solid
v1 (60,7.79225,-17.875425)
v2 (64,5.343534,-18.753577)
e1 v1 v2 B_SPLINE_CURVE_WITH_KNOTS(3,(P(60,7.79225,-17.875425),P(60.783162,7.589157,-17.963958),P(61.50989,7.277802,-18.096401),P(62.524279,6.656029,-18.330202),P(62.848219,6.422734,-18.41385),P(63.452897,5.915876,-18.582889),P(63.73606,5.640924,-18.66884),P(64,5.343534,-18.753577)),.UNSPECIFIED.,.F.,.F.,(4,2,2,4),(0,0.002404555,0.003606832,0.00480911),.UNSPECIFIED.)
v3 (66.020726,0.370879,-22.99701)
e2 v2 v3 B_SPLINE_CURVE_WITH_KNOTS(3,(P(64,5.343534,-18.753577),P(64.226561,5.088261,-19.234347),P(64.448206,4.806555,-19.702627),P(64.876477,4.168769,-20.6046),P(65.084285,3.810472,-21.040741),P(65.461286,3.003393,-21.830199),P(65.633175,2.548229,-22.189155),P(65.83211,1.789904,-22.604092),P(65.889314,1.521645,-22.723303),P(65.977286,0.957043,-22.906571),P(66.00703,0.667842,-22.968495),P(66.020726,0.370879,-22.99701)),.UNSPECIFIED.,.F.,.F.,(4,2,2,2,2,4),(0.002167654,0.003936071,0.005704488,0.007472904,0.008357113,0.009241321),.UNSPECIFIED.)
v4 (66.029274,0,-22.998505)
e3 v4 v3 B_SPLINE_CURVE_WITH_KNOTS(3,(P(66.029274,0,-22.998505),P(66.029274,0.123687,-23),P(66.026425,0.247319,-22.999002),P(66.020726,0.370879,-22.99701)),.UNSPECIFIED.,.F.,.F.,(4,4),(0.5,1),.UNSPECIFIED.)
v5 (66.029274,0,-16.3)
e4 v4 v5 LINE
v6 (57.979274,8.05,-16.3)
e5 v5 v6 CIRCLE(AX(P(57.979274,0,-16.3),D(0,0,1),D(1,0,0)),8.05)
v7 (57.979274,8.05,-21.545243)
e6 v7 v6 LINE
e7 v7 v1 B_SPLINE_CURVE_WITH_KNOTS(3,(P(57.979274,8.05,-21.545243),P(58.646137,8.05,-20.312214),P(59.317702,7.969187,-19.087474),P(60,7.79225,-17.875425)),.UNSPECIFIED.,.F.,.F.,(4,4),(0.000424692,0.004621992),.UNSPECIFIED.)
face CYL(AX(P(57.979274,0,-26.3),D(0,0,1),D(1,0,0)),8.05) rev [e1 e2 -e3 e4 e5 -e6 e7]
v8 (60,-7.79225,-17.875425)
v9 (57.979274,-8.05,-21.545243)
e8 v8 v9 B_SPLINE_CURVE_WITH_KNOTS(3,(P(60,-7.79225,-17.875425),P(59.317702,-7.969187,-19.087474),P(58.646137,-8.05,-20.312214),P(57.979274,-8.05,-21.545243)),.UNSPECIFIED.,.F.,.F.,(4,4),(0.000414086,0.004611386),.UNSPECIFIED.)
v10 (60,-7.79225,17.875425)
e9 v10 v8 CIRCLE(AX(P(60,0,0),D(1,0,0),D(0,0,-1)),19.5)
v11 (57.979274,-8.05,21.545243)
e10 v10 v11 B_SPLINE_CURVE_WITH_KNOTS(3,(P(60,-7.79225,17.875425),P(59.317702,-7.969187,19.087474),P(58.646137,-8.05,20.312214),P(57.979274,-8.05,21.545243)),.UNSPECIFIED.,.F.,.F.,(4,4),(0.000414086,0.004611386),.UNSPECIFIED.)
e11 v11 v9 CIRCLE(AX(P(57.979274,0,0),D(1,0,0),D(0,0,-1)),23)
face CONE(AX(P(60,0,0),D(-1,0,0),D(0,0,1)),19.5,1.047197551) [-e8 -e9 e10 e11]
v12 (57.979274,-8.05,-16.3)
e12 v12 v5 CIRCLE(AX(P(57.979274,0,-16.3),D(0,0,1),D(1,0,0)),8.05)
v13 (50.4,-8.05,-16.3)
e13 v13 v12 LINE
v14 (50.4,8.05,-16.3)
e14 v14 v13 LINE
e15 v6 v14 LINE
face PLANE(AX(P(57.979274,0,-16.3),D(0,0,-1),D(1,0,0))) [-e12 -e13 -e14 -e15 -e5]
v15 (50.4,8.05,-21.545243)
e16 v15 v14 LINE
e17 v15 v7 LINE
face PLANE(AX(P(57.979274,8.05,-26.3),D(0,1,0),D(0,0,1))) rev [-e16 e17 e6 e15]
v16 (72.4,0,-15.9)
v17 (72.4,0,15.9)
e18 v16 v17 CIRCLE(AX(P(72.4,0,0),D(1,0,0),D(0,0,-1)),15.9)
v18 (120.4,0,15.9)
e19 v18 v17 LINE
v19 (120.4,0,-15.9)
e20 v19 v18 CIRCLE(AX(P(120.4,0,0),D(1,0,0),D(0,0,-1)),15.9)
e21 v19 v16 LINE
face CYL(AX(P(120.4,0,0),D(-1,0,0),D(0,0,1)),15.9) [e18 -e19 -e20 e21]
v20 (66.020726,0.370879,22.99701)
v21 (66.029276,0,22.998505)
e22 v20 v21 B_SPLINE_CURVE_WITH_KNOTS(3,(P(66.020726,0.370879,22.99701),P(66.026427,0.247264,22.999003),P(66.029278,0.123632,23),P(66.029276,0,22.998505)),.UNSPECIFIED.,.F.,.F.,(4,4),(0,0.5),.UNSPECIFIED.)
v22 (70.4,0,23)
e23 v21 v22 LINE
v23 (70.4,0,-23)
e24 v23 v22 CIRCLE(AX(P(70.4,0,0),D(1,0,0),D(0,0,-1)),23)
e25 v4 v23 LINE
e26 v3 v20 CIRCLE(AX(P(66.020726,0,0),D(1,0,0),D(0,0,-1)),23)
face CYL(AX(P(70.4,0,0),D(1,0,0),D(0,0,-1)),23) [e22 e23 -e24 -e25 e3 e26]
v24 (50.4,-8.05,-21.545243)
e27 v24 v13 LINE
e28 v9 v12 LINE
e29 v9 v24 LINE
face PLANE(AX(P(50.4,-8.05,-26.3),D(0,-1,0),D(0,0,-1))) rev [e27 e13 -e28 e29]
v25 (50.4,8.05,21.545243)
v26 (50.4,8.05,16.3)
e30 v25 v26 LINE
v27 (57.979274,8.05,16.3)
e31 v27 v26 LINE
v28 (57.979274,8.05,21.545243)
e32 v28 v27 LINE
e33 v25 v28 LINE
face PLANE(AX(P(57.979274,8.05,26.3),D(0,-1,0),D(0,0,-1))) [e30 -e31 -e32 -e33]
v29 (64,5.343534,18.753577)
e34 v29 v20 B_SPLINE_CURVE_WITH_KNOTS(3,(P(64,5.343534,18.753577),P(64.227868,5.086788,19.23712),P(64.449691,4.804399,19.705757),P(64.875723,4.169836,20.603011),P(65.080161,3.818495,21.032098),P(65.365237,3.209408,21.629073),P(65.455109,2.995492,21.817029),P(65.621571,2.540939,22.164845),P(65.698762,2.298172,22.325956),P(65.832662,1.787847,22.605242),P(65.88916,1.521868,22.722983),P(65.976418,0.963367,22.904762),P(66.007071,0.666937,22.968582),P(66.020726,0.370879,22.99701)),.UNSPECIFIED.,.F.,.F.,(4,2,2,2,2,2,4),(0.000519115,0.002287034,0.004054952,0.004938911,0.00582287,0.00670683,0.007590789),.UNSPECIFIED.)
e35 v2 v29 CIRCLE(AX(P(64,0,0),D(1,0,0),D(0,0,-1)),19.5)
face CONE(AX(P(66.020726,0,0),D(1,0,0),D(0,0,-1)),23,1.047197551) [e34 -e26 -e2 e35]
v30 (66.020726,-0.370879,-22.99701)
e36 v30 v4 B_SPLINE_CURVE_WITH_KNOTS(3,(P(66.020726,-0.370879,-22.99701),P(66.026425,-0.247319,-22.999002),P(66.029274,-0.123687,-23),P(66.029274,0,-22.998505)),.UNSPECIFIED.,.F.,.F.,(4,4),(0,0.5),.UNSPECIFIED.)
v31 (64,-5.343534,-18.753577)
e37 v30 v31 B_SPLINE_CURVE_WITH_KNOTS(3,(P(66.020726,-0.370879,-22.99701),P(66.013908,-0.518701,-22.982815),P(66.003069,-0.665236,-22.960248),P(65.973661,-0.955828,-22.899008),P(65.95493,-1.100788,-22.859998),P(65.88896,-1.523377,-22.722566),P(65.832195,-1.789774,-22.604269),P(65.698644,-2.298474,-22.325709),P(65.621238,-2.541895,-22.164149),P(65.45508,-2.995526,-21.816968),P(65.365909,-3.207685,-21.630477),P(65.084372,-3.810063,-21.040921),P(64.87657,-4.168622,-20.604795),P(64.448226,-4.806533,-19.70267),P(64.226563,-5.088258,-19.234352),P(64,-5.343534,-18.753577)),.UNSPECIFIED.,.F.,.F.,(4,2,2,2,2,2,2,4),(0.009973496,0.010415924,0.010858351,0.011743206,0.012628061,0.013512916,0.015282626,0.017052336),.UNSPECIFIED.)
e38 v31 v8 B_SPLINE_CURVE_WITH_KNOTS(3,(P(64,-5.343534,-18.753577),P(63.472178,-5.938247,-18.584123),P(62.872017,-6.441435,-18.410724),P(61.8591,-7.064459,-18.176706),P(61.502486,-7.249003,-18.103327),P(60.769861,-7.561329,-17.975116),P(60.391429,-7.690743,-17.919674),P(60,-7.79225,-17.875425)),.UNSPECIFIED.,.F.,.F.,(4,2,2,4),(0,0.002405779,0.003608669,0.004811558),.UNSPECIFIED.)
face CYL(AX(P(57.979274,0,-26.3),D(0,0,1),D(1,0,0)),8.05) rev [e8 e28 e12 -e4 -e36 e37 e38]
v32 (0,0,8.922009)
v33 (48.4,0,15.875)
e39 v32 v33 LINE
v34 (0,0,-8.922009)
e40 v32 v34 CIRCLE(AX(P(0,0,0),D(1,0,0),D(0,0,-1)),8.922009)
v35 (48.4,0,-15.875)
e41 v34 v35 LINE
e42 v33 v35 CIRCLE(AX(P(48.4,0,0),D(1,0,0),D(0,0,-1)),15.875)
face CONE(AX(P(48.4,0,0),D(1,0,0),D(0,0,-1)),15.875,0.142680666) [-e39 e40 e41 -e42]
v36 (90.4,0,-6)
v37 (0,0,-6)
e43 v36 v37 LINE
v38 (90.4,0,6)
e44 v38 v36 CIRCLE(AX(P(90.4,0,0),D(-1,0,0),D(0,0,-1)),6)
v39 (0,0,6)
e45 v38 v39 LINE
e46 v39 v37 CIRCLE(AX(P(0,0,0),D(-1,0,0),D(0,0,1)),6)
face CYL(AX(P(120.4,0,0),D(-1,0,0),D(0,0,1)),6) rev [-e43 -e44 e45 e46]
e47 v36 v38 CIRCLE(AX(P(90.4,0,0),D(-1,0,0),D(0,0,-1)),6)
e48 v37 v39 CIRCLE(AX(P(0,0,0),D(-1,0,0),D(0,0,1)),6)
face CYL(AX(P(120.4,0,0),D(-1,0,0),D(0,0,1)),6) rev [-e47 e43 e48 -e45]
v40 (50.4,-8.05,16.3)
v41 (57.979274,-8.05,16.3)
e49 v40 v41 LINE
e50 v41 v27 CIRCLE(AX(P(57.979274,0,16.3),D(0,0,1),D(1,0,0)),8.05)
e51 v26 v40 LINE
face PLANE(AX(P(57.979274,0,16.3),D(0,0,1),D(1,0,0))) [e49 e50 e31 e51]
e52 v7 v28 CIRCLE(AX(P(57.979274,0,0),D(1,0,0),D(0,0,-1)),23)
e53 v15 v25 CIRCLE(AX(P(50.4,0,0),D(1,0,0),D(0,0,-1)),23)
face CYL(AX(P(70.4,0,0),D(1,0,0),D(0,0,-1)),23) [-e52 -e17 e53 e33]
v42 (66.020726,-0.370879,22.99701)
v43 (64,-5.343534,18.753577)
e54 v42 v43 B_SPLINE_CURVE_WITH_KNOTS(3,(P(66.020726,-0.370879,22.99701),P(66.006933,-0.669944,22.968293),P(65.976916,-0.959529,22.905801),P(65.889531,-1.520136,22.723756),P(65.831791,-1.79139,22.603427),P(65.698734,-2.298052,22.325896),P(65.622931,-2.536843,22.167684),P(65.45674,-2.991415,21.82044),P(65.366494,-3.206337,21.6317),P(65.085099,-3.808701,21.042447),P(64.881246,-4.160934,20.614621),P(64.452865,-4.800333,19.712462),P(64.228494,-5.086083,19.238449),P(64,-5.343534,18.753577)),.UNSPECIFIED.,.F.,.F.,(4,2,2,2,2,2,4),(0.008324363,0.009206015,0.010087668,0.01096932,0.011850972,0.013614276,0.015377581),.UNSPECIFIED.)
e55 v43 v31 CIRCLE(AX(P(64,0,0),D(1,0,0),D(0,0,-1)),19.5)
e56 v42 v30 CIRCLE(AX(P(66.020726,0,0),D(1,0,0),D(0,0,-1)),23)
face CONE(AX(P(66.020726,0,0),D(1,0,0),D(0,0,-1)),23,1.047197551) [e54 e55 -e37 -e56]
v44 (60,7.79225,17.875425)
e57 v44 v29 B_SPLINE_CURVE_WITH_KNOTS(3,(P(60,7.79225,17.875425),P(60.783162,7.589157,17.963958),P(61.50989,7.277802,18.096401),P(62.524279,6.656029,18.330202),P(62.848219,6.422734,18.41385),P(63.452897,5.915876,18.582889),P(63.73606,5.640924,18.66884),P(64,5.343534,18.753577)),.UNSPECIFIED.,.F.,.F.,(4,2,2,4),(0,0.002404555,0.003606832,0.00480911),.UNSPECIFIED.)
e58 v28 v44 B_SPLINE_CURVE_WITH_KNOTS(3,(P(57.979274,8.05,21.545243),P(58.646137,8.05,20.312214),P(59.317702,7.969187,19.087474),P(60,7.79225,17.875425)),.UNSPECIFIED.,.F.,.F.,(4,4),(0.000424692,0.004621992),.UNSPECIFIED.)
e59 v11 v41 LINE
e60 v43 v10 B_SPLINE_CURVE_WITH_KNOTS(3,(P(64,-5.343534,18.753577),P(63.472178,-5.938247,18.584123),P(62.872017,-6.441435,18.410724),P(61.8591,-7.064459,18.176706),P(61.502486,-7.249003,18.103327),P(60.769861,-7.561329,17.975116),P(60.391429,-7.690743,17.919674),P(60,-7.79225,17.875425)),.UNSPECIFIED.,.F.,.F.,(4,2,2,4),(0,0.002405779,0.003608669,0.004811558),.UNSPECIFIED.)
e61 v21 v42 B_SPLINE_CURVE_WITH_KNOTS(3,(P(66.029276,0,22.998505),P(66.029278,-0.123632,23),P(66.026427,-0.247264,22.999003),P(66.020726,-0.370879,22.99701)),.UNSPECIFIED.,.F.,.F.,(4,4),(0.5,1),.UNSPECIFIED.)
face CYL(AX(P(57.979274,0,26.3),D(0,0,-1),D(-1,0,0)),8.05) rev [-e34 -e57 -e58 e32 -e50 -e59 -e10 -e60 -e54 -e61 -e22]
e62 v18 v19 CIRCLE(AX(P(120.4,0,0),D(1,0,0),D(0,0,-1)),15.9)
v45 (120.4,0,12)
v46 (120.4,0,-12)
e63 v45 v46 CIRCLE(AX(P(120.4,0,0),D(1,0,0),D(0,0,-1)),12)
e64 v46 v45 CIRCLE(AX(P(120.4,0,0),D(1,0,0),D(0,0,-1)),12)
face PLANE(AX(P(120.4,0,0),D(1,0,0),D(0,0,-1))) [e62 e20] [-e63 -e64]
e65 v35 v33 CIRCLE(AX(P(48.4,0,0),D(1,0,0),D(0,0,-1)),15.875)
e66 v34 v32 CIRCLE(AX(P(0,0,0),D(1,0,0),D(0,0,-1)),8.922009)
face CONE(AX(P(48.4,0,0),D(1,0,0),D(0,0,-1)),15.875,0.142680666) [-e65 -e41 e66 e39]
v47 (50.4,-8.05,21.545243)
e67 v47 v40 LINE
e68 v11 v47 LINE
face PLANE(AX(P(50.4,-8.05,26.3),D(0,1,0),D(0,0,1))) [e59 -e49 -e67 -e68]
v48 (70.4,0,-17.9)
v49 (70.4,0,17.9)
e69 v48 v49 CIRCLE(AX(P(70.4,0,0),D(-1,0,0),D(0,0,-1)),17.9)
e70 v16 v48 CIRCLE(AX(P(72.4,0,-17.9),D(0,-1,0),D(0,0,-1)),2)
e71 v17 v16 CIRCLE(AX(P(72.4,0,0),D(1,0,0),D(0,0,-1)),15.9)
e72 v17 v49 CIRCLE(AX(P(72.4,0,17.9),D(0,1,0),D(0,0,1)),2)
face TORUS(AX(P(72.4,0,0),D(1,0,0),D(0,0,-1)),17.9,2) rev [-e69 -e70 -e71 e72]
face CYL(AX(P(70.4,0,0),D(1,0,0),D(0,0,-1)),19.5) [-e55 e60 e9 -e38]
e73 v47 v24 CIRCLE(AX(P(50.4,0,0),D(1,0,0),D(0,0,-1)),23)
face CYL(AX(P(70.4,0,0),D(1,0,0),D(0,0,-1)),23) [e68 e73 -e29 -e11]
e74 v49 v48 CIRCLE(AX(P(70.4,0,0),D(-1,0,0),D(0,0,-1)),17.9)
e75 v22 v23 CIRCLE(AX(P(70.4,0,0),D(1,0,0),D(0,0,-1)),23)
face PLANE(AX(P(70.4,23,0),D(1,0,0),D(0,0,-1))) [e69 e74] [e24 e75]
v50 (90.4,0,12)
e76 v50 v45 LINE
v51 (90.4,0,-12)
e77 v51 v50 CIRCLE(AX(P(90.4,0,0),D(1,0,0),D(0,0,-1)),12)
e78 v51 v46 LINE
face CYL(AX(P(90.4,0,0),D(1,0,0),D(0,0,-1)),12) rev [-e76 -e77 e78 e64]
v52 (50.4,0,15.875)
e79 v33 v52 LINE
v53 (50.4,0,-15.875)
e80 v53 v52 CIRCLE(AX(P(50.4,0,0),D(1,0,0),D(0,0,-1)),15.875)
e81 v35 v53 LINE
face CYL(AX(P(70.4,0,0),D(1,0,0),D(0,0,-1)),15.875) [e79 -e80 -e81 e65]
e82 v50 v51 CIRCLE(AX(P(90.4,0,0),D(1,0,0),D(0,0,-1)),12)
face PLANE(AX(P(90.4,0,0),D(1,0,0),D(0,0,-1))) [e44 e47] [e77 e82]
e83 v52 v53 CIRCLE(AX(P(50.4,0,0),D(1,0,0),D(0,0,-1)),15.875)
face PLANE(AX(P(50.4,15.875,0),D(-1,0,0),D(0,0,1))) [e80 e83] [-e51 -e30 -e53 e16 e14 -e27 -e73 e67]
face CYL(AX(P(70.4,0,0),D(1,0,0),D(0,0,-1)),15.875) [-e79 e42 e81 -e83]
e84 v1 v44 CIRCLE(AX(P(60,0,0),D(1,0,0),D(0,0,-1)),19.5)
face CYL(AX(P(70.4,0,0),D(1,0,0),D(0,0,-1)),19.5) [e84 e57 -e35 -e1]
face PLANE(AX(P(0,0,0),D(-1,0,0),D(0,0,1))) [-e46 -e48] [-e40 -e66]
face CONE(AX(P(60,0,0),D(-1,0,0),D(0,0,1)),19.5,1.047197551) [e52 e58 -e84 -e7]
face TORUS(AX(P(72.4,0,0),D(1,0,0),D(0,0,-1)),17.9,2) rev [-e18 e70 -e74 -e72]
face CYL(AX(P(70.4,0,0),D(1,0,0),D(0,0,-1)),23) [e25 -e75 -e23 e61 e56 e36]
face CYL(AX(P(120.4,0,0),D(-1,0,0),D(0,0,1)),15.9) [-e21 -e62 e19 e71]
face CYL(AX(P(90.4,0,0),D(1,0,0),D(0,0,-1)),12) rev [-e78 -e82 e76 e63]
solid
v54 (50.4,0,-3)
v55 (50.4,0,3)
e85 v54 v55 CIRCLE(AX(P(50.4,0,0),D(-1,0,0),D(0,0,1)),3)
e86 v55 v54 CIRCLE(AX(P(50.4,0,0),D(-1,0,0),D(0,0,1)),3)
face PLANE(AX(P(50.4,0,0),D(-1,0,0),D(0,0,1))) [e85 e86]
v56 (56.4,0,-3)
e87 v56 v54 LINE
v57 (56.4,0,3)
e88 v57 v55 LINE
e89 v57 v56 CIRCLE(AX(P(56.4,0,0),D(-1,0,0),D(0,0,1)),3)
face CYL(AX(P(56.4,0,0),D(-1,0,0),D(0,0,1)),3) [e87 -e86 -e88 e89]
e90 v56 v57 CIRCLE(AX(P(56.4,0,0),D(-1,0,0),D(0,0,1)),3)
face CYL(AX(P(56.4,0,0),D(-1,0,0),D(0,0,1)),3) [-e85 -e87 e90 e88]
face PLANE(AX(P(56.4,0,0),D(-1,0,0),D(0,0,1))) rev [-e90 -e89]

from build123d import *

# Parameters (mm, degrees)
CUT_EXTRUDE_1_DEPTH = 10
SKETCH_4_R          = 15.9
EXTRUDE_1_DEPTH     = 50
FILLET_1_R          = 2
SKETCH_5_R          = 6
CUT_EXTRUDE_2_DEPTH = 125.716318135
SKETCH_6_R          = 12
CUT_EXTRUDE_3_DEPTH = 30
SKETCH_7_R          = 3
EXTRUDE_2_DEPTH     = 6


with BuildPart() as part:
    # 草图1 → 旋转1 (revolve)
    with BuildSketch(Plane.XY, mode=Mode.PRIVATE) as revolve_1_sk:
        Polygon((0, 0), (0, 8.92200912), (48.4, 15.875), (50.4, 15.875), (50.4, 23), (57.979274058, 23), (60, 19.5), (64, 19.5), (66.020725942, 23), (70.4, 23), (70.4, 0), align=None)
    revolve(revolve_1_sk.sketch.rotate(Axis((70.4, 0, 0), (-1, 0, 0)), 90), axis=Axis((70.4, 0, 0), (-1, 0, 0)))

    # 草图2 → 切除-拉伸1 (cut)
    with BuildSketch(Plane.XY.offset(16.3)):
        with BuildLine():
            Line((57.979274058, 8.05), (50.4, 8.05))
            Line((50.4, 8.05), (50.4, -8.05))
            Line((50.4, -8.05), (57.979274058, -8.05))
            ThreePointArc((57.979274058, -8.05), (66.029274058, 0), (57.979274058, 8.05))
        make_face()
    cut_extrude_1 = extrude(amount=CUT_EXTRUDE_1_DEPTH, mode=Mode.SUBTRACT)

    # 镜向1: 切除-拉伸1 across plane
    add(cut_extrude_1.mirror(Plane.XY), mode=Mode.SUBTRACT)

    # 草图4 → 凸台-拉伸1 (add)
    with BuildSketch(Plane(origin=(70.4, 0, 0), x_dir=(0, 0, -1), z_dir=(1, 0, 0))):
        Circle(SKETCH_4_R)
    extrude(amount=EXTRUDE_1_DEPTH)

    # 圆角1
    fillet_1_edges = [part.edges().sort_by_distance(p)[0] for p in [
        (70.4, 0, 15.9),
    ]]
    fillet(fillet_1_edges, radius=FILLET_1_R)

    # 草图5 → 切除-拉伸2 (cut, through all)
    with BuildSketch(Plane.ZY):
        Circle(SKETCH_5_R)
    extrude(amount=-CUT_EXTRUDE_2_DEPTH, mode=Mode.SUBTRACT)

    # 草图6 → 切除-拉伸3 (cut)
    with BuildSketch(Plane(origin=(120.4, 0, 0), x_dir=(0, 0, -1), z_dir=(1, 0, 0))):
        Circle(SKETCH_6_R)
    extrude(amount=-CUT_EXTRUDE_3_DEPTH, mode=Mode.SUBTRACT)


with BuildPart() as body_2:
    # 草图7 → 凸台-拉伸2 (new body)
    with BuildSketch(Plane.ZY.offset(-50.4)):
        Circle(SKETCH_7_R)
    extrude(amount=-EXTRUDE_2_DEPTH)


solid = Compound([part.part, body_2.part])
